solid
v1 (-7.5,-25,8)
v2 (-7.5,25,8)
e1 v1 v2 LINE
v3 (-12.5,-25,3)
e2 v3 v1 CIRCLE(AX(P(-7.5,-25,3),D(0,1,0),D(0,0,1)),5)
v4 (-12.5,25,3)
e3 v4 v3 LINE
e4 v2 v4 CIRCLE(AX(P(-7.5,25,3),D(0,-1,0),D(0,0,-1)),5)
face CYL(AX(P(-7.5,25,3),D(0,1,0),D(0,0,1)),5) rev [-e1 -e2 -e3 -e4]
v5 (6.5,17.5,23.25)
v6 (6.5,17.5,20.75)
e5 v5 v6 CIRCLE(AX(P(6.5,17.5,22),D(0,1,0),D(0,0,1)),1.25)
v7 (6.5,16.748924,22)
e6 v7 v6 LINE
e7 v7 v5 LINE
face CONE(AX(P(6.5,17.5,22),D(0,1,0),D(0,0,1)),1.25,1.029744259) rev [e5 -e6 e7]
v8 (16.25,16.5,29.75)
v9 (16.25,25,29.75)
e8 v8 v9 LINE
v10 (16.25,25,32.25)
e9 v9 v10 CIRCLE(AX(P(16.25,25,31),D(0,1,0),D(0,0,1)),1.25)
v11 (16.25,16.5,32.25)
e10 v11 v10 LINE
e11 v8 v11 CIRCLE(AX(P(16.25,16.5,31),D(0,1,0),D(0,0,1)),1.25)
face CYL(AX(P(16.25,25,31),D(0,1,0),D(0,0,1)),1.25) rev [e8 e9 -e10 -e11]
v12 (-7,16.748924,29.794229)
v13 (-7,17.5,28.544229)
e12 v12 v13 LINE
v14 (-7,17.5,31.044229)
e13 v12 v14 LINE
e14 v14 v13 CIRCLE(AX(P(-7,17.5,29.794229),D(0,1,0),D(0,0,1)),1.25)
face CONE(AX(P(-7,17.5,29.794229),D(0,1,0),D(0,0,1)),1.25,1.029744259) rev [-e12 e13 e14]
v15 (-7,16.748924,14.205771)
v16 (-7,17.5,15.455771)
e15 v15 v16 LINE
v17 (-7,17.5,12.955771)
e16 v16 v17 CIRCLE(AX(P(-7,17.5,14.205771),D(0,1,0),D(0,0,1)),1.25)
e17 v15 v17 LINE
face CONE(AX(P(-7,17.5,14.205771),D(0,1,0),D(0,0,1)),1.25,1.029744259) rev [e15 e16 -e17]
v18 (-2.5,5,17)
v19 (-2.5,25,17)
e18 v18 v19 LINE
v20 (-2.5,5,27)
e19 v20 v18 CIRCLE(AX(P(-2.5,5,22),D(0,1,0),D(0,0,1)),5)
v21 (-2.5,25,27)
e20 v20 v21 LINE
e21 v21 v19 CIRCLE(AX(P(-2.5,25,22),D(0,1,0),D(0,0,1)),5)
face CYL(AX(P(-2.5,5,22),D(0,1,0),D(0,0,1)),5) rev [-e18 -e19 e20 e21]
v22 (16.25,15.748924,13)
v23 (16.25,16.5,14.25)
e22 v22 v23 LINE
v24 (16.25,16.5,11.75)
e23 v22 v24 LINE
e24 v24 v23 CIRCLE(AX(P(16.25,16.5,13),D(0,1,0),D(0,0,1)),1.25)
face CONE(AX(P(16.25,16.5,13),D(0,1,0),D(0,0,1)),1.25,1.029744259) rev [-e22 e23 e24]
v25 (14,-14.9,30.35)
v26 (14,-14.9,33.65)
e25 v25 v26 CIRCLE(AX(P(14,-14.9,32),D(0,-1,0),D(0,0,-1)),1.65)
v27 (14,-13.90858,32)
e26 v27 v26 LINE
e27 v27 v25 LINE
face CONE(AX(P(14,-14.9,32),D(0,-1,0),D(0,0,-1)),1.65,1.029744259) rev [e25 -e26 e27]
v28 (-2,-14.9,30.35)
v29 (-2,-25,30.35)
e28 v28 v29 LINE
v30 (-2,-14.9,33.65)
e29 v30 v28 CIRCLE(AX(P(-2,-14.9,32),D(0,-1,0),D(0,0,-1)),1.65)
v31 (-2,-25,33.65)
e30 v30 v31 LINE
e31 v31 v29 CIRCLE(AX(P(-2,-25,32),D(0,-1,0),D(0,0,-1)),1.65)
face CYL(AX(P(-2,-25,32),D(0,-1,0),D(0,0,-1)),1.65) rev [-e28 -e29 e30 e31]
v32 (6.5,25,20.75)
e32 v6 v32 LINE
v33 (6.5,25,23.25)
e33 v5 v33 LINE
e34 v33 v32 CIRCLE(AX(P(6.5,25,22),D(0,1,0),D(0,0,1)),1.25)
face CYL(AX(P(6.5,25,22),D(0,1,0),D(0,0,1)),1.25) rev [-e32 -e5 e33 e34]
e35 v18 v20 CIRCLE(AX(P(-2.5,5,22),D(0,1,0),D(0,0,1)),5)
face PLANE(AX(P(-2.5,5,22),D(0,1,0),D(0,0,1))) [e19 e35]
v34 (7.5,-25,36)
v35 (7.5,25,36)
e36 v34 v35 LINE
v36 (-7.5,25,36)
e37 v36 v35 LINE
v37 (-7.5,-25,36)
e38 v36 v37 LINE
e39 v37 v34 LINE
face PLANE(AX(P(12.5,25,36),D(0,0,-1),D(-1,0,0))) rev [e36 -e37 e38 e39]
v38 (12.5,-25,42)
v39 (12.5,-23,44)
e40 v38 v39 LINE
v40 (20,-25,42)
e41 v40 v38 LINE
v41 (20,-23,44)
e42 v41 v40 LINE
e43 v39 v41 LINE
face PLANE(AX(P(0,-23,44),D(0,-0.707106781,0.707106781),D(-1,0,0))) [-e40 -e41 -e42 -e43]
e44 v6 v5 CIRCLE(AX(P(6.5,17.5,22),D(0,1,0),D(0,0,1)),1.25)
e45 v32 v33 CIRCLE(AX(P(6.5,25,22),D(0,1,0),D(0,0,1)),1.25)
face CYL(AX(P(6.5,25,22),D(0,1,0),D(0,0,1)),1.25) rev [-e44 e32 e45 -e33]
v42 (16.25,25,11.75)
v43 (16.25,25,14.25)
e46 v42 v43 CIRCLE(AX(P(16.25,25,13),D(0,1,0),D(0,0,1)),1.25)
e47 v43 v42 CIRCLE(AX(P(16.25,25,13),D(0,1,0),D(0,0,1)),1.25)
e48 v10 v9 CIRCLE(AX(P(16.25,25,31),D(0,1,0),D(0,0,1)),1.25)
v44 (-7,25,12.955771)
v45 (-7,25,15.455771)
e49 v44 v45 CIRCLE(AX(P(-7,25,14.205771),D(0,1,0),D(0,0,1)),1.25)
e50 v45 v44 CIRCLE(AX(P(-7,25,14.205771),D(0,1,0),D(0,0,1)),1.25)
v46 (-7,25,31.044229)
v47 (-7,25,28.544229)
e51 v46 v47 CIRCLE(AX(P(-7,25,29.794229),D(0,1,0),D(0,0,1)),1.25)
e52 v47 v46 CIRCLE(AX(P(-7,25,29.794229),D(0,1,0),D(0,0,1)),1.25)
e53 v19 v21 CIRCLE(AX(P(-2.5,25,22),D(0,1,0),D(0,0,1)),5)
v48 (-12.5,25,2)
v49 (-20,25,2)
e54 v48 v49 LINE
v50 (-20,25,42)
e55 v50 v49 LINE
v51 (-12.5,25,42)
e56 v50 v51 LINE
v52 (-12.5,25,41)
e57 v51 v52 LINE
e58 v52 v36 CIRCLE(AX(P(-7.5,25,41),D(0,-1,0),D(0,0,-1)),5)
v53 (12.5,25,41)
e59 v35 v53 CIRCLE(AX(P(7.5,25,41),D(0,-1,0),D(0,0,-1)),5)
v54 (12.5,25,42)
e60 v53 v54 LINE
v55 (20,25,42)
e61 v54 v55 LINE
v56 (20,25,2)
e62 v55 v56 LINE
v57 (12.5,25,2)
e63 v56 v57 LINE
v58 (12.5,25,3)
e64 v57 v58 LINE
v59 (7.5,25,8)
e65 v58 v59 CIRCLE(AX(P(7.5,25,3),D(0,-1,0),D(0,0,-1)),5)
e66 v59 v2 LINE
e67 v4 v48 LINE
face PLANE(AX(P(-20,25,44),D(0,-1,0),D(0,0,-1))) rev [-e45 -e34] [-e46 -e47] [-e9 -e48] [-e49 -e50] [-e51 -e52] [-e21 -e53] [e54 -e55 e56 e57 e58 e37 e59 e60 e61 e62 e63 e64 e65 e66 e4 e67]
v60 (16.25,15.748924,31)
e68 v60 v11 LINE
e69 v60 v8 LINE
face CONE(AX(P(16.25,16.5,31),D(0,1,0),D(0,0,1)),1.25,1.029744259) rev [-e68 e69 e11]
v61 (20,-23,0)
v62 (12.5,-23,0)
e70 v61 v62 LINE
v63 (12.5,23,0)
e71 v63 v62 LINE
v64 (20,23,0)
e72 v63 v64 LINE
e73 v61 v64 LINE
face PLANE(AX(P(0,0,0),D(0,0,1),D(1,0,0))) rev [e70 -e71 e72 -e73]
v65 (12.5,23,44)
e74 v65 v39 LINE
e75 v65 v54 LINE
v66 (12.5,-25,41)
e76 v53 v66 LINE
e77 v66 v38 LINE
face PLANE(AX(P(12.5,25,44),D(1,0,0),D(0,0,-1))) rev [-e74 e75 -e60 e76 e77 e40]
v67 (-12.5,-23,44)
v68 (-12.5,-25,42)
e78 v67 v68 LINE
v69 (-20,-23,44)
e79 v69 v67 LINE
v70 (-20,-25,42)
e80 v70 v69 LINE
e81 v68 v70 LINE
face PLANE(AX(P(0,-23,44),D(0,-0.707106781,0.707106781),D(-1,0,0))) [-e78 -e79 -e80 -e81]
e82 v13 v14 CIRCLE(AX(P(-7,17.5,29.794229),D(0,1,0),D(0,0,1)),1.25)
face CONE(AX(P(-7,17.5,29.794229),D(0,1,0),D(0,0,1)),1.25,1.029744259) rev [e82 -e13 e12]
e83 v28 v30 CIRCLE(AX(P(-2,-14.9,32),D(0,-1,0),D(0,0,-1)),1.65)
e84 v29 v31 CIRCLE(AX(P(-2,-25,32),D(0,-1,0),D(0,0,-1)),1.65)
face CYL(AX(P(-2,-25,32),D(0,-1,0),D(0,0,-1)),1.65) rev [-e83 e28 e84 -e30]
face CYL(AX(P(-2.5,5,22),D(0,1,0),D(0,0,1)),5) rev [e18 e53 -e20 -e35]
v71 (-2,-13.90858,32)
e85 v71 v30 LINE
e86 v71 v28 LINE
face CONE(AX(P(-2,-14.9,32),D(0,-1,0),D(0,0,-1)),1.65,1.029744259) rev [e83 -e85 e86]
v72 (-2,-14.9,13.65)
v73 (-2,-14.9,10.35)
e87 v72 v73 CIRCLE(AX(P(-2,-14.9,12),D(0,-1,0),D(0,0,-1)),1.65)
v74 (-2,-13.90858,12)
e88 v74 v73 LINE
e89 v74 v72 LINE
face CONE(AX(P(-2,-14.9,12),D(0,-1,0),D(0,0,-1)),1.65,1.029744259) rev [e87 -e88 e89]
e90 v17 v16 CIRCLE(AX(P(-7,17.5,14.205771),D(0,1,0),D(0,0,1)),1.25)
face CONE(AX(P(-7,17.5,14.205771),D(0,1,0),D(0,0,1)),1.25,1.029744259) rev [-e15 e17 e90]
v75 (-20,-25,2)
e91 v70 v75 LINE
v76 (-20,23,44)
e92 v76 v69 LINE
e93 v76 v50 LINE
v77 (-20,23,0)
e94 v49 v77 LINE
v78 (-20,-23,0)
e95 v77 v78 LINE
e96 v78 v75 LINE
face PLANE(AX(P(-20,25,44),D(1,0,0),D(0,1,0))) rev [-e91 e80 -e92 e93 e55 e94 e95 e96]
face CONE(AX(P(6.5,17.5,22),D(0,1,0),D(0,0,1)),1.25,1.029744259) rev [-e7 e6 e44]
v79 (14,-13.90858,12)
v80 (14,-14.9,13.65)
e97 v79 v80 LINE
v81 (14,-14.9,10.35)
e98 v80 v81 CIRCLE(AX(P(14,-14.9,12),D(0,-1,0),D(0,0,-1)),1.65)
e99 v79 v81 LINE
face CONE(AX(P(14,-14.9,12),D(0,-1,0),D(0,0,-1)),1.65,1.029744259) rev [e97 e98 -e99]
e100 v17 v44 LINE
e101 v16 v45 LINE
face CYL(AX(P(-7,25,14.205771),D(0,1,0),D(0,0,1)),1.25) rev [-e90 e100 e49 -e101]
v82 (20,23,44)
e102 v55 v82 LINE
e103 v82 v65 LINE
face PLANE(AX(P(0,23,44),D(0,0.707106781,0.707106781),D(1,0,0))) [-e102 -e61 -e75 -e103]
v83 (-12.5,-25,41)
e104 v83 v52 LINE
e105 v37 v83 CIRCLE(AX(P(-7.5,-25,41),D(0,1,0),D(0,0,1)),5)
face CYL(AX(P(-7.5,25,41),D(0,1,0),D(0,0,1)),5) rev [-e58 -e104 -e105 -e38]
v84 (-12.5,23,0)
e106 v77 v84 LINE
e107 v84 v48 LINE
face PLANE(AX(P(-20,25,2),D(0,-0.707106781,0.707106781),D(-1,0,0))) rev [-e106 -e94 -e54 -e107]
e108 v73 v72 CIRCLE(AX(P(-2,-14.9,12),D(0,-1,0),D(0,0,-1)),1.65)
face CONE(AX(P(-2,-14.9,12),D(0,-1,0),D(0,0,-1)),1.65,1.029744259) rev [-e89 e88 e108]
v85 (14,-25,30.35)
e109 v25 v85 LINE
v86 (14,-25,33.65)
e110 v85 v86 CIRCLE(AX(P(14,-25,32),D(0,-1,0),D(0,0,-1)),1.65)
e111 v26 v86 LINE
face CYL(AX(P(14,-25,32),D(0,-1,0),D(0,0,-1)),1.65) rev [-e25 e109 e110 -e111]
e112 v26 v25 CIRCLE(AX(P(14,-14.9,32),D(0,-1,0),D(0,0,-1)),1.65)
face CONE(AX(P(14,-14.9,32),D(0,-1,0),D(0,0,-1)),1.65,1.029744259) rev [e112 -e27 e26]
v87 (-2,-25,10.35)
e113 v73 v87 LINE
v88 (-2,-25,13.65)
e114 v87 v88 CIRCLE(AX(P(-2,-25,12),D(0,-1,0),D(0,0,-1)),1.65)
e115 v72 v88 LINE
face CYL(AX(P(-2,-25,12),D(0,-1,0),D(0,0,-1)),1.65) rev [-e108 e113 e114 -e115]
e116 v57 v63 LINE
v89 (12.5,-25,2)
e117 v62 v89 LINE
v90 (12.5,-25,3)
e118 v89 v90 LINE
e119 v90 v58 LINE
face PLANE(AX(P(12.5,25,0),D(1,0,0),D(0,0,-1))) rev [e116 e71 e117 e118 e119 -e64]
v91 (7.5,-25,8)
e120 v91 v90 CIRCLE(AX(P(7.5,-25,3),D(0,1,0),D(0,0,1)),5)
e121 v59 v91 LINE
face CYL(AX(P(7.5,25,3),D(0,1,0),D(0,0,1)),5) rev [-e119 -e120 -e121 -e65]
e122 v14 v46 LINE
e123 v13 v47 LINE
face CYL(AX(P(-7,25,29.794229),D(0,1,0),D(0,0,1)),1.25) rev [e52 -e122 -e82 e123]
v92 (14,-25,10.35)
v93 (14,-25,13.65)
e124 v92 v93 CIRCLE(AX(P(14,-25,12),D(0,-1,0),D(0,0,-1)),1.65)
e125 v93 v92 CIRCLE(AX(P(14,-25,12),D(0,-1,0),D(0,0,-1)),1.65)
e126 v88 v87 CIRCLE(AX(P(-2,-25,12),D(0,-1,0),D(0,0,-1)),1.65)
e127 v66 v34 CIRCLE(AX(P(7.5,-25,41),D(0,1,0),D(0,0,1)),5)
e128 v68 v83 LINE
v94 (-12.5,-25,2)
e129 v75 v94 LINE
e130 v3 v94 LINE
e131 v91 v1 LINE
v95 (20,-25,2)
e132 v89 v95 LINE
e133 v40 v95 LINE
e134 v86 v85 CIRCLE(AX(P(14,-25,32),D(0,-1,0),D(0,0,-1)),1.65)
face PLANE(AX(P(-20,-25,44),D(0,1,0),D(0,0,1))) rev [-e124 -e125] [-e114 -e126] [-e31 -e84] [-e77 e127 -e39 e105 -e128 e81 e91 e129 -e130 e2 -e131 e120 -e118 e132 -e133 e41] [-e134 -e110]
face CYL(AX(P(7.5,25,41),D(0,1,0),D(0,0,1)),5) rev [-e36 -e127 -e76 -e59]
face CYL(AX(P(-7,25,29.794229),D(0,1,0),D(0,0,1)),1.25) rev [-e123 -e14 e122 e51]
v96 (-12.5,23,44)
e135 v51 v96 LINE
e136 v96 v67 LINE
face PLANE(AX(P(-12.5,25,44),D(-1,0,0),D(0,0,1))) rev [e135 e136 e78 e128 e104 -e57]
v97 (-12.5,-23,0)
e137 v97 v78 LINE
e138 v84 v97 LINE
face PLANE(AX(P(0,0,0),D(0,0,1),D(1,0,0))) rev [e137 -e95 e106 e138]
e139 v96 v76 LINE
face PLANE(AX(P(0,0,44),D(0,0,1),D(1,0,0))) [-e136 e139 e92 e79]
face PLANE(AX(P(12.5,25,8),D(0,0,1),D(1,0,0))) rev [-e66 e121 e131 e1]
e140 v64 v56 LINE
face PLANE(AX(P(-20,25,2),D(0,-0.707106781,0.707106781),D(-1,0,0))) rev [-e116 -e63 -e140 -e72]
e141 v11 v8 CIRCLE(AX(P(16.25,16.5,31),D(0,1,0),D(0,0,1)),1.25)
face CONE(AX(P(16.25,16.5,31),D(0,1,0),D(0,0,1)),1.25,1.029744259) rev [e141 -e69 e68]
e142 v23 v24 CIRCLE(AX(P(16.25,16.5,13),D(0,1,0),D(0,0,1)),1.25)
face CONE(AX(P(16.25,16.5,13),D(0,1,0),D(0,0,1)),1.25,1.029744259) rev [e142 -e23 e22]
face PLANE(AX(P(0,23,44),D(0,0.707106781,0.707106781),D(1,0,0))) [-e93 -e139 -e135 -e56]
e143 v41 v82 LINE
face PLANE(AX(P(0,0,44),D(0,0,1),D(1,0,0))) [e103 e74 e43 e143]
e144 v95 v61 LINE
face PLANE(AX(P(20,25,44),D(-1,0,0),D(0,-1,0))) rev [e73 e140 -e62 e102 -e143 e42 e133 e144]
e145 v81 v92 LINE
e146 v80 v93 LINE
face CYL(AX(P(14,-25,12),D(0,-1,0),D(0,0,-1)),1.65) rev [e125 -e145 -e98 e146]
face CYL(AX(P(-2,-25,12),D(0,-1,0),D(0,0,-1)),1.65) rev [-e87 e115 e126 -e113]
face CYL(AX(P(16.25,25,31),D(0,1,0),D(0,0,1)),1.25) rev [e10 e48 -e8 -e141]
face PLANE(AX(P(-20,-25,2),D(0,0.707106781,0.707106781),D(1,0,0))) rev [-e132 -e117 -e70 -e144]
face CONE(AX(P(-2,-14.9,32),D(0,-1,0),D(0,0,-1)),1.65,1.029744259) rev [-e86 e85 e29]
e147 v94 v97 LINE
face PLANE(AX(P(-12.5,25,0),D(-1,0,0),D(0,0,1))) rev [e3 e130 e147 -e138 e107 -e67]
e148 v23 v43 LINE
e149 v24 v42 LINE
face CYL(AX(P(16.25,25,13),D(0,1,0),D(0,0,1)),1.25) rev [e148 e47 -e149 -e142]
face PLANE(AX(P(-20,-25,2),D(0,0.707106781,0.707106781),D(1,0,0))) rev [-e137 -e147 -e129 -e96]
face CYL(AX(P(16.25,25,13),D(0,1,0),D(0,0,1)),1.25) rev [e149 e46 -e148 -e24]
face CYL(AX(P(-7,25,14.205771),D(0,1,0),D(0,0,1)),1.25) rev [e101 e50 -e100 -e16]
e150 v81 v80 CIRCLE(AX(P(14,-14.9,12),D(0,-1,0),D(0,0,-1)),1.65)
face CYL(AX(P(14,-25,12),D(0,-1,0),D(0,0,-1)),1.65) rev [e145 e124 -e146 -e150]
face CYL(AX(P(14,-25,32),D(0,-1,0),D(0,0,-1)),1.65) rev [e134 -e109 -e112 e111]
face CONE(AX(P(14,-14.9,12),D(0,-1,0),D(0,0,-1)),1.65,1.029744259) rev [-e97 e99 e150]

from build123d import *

# Parameters (mm, degrees)
SKETCH1_W             = 40
SKETCH1_H             = 50
BOSS_EXTRUDE1_DEPTH   = 44
SKETCH2_R             = 5
CUT_EXTRUDE1_DEPTH    = 20
CIRPATTERN1_COUNT     = 3
M4_TAPPED_HOLE1_D     = 3.3
M4_TAPPED_HOLE1_DEPTH = 10.1
M4_TAPPED_HOLE1_TIP   = 0.991420021
SKETCH7_W             = 25
SKETCH7_H             = 8
CUT_EXTRUDE2_DEPTH    = 70.541354603
CHAMFER1_SIZE         = 2
FILLET1_R             = 5
M3_TAPPED_HOLE2_D     = 2.5
M3_TAPPED_HOLE2_DEPTH = 8.5
M3_TAPPED_HOLE2_TIP   = 0.751075774


with BuildPart() as part:
    # Sketch1 → Boss-Extrude1 (new body)
    with BuildSketch(Plane.XY):
        Rectangle(SKETCH1_W, SKETCH1_H)
    extrude(amount=BOSS_EXTRUDE1_DEPTH)

    # Sketch2 → Cut-Extrude1 (cut)
    with BuildSketch(Plane(origin=(0, 25, 0), x_dir=(1, 0, 0), z_dir=(0, 1, 0))):
        with Locations(Location((-2.5, -22, 0), (0, 0, 270))):
            Circle(SKETCH2_R)
    extrude(amount=-CUT_EXTRUDE1_DEPTH, mode=Mode.SUBTRACT)

    # Sketch3 → M3 Tapped Hole1 (revolve, cut)
    with BuildSketch(Plane(origin=(6.5, 25, 22), x_dir=(0, 0, 1), z_dir=(1, 0, 0))):
        Polygon((0, 0), (0, 8.251075774), (1.25, 7.5), (1.25, 0), align=None)
    m3_tapped_hole1 = revolve(axis=Axis((6.5, 31.35, 22), (0, -1, 0)), mode=Mode.SUBTRACT)

    # CirPattern1: M3 Tapped Hole1 ×3 about axis
    cirpattern1_axis = Axis((-2.5, 0, 22), (0, 1, 0))
    for i in range(1, CIRPATTERN1_COUNT):
        add(m3_tapped_hole1.rotate(cirpattern1_axis, i * 360 / CIRPATTERN1_COUNT), mode=Mode.SUBTRACT)

    # M4 Tapped Hole1
    with Locations(Plane(origin=(0, -25, 0), x_dir=(-1, 0, 0), z_dir=(0, -1, 0))):
        with Locations((-14, -32), (2, -32), (-14, -12), (2, -12)):
            Hole(M4_TAPPED_HOLE1_D / 2, depth=M4_TAPPED_HOLE1_DEPTH)
            with Locations((0, 0, -(M4_TAPPED_HOLE1_DEPTH + M4_TAPPED_HOLE1_TIP / 2))):  # 118° drill point
                Cone(0, M4_TAPPED_HOLE1_D / 2, M4_TAPPED_HOLE1_TIP, mode=Mode.SUBTRACT)

    # Sketch7 → Cut-Extrude2 (cut, through all)
    with BuildSketch(Plane.XZ.offset(25)):
        with Locations((0, 40)):
            Rectangle(SKETCH7_W, SKETCH7_H)
        with Locations((0, 4)):
            Rectangle(SKETCH7_W, SKETCH7_H)
    extrude(amount=-CUT_EXTRUDE2_DEPTH, mode=Mode.SUBTRACT)

    # Chamfer1
    chamfer1_edges = [part.edges().sort_by_distance(p)[0] for p in [
        (-16.25, -25, 44),
        (-16.25, -25, 0),
        (-16.25, 25, 44),
        (16.25, -25, 44),
        (16.25, 25, 0),
        (16.25, -25, 0),
        (-16.25, 25, 0),
        (16.25, 25, 44),
    ]]
    chamfer(chamfer1_edges, length=CHAMFER1_SIZE)

    # Fillet1
    fillet1_edges = [part.edges().sort_by_distance(p)[0] for p in [
        (12.5, 0, 36),
        (-12.5, 0, 36),
        (12.5, 0, 8),
        (-12.5, 0, 8),
    ]]
    fillet(fillet1_edges, radius=FILLET1_R)

    # M3 Tapped Hole2
    with Locations(Plane(origin=(0, 25, 0), x_dir=(1, 0, 0), z_dir=(0, 1, 0))):
        with Locations((16.25, -31), (16.25, -13)):
            Hole(M3_TAPPED_HOLE2_D / 2, depth=M3_TAPPED_HOLE2_DEPTH)
            with Locations((0, 0, -(M3_TAPPED_HOLE2_DEPTH + M3_TAPPED_HOLE2_TIP / 2))):  # 118° drill point
                Cone(0, M3_TAPPED_HOLE2_D / 2, M3_TAPPED_HOLE2_TIP, mode=Mode.SUBTRACT)


solid = part.part
